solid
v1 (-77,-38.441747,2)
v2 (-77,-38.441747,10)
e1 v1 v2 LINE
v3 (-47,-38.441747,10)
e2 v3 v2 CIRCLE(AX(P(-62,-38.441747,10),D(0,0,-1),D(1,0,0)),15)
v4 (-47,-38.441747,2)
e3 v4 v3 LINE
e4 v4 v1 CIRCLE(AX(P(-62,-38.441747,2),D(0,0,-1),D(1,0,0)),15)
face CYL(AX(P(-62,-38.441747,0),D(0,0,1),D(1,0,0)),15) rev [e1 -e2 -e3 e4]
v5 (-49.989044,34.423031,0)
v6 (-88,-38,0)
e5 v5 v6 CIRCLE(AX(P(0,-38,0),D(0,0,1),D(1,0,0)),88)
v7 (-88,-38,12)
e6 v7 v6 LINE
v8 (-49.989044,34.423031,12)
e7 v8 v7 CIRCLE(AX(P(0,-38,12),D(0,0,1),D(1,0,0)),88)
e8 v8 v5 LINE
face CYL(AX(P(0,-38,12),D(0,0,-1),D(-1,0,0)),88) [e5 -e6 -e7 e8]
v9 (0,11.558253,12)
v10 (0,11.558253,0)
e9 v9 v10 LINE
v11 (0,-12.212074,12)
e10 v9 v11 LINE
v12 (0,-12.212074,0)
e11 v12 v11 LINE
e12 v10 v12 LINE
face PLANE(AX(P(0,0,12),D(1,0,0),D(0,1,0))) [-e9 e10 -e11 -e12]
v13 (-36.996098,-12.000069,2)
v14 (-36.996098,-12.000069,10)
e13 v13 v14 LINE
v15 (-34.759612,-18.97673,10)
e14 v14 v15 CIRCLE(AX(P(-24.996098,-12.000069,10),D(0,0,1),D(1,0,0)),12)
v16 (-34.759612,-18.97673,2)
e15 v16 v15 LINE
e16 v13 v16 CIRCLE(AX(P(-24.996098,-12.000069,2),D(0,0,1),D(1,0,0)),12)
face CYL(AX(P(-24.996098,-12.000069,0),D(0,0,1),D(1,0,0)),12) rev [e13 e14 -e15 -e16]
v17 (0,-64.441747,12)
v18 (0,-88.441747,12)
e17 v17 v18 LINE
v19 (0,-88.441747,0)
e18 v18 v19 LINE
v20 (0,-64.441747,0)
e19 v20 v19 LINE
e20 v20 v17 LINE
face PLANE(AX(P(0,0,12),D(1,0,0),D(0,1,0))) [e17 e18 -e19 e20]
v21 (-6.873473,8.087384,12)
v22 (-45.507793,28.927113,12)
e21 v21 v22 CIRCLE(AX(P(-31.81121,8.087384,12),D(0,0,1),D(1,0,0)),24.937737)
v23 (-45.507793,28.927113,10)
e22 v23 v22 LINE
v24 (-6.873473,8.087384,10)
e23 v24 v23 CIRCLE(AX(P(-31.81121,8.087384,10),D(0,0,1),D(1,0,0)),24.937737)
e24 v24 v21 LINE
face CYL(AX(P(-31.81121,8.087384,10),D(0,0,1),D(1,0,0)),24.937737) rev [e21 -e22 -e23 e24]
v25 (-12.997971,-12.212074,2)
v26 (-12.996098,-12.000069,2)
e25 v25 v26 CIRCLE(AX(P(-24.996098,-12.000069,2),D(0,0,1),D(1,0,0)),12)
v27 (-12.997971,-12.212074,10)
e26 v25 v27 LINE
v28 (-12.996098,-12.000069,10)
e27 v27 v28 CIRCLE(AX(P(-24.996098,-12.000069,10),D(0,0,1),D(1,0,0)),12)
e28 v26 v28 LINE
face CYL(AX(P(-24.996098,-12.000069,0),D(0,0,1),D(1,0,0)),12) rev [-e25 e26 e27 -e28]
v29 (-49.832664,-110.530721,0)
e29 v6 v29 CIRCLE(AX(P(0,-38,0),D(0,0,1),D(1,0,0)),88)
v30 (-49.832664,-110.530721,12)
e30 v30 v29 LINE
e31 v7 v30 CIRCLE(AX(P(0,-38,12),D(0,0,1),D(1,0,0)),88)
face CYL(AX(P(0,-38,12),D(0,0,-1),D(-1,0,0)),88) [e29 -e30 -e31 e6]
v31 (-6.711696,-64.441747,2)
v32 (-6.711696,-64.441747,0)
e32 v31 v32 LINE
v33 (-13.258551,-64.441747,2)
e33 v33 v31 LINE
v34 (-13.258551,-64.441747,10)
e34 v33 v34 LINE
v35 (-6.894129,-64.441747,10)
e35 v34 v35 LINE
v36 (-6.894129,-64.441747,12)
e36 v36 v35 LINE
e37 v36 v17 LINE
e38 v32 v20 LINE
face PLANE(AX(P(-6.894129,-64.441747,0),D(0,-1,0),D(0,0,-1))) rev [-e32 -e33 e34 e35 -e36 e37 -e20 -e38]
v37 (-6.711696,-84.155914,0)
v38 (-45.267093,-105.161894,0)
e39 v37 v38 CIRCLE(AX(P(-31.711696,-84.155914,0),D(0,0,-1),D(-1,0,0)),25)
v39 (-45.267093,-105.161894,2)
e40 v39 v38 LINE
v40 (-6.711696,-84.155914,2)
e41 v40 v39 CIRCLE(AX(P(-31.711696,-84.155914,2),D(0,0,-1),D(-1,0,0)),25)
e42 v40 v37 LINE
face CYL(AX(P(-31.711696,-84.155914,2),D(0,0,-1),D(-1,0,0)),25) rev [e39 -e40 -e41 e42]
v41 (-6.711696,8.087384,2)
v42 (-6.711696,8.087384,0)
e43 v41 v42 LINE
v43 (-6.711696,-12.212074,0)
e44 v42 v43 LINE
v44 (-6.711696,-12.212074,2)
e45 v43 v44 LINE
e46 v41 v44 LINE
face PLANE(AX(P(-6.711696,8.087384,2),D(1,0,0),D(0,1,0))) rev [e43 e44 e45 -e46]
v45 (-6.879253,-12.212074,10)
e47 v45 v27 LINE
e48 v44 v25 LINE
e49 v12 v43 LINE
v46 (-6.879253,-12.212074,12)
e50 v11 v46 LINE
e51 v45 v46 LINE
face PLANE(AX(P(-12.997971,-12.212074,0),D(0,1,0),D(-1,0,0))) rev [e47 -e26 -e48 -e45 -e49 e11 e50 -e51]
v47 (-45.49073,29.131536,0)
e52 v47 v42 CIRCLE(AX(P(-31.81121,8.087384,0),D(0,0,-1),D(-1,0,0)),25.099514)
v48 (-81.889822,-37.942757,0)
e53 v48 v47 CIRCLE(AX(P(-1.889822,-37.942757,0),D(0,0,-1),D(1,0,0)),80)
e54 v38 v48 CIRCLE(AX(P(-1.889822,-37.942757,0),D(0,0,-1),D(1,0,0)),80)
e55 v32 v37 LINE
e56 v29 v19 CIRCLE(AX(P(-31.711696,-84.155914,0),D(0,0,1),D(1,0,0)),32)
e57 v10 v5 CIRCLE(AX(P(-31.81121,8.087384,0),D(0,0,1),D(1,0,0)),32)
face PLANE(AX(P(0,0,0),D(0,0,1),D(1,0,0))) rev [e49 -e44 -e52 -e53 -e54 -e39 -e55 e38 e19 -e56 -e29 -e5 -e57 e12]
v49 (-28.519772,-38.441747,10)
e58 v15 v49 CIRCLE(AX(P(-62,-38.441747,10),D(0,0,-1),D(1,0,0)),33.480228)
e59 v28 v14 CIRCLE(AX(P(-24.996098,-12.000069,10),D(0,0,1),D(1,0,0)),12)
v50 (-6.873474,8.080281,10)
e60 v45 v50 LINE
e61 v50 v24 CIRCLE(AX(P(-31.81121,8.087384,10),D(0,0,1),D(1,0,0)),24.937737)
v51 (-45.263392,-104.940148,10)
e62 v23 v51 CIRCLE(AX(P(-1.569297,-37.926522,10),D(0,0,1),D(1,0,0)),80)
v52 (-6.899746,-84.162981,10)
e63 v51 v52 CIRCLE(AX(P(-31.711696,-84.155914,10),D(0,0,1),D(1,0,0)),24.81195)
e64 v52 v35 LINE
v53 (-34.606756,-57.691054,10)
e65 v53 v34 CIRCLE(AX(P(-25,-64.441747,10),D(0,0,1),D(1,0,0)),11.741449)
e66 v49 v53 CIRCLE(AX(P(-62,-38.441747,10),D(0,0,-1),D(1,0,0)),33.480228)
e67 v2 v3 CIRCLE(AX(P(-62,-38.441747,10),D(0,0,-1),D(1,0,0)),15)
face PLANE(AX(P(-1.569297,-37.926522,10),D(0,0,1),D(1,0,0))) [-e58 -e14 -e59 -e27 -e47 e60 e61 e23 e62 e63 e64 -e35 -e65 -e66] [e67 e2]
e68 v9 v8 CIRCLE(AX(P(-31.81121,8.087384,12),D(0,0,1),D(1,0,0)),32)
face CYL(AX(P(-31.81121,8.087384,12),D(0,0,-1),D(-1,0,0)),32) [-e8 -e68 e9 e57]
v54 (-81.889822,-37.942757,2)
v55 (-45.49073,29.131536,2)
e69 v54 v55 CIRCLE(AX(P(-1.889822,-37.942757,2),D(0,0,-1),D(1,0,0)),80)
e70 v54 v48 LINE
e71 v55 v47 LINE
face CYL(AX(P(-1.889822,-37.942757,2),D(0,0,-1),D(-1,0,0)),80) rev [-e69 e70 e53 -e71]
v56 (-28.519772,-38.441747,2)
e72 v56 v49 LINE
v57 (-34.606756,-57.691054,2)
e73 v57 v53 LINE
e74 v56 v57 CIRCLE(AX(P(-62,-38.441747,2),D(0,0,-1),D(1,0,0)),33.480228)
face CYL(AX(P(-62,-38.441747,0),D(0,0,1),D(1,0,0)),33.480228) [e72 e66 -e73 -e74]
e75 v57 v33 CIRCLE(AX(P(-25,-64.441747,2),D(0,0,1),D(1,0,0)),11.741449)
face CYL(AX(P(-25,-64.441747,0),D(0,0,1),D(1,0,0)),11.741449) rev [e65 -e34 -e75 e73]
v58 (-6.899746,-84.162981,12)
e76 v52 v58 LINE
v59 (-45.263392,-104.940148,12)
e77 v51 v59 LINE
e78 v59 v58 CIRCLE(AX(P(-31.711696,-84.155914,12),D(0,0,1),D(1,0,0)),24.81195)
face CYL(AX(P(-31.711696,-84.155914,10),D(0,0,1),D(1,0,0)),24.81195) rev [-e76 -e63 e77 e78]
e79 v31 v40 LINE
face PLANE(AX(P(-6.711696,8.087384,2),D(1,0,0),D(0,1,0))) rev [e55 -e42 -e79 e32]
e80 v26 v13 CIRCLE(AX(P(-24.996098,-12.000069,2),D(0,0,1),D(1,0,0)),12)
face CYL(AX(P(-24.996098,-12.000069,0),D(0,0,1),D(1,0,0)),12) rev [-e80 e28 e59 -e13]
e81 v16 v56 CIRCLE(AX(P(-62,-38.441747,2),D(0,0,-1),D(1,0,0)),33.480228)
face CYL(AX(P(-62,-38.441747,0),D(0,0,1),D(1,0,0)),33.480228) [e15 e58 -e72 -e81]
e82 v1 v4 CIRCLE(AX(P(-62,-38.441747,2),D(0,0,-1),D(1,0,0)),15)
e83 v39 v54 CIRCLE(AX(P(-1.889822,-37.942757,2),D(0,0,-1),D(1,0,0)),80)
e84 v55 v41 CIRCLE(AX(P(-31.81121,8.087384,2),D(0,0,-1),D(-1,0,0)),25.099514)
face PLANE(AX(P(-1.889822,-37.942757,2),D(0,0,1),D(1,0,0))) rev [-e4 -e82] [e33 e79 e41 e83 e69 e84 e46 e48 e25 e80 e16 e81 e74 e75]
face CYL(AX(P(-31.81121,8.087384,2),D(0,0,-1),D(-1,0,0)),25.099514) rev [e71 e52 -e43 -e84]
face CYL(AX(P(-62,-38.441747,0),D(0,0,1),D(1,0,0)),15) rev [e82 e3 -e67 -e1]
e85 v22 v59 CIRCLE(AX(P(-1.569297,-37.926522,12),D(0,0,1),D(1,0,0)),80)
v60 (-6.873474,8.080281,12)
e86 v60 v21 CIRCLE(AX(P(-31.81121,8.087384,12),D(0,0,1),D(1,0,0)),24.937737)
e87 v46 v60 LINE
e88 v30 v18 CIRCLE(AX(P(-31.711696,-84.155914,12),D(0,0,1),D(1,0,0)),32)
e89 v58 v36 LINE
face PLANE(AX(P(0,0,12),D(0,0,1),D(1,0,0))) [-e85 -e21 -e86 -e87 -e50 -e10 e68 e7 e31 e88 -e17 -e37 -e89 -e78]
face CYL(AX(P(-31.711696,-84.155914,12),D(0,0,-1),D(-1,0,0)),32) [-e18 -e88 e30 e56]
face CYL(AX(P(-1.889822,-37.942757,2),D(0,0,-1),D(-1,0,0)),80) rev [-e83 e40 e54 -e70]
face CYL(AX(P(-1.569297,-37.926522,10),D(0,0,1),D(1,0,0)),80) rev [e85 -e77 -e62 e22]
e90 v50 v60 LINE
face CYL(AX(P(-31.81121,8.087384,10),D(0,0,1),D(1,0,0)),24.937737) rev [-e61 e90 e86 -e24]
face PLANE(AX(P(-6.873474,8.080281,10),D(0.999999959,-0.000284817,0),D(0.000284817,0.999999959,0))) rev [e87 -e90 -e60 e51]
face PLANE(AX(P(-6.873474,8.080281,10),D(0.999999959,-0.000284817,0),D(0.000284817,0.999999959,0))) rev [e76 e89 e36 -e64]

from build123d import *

# Parameters (mm, degrees)
PLATE_BODY_12MM_DEPTH   = 12
THROUGH_HOLE_SKETCH_R   = 15
THROUGH_HOLE_DEPTH      = 12
FACE_POCKET_A_2MM_DEPTH = 2
FACE_POCKET_B_2MM_DEPTH = 2
SLOT_OPENING_CUT_DEPTH  = 10
RIM_NOTCH_A_SKETCH_W    = 6.711695518
RIM_NOTCH_A_SKETCH_H    = 52.229672595
RIM_NOTCH_A_DEPTH       = 10
RIM_NOTCH_B_SKETCH_W    = 2
RIM_NOTCH_B_SKETCH_H    = 52.229672595
RIM_NOTCH_B_DEPTH       = 10


with BuildPart() as part:
    # Plate Outline Sketch → Plate Body 12mm (new body)
    with BuildSketch(Plane.XY):
        with BuildLine():
            Line((0, -76), (0, 0))
            Line((0, 0), (0, 11.558252986))
            ThreePointArc((0, 11.558252986), (-10.446142685, 31.91035387), (-31.811209757, 40.087383673))
            ThreePointArc((-31.811209757, 40.087383673), (-41.331169578, 38.638494373), (-49.989043904, 34.423031486))
            ThreePointArc((-49.989043904, 34.423031486), (-87.99994879, -38.094936415), (-49.832664385, -110.530721493))
            ThreePointArc((-49.832664385, -110.530721493), (-41.198690561, -114.717276949), (-31.711695518, -116.155913677))
            ThreePointArc((-31.711695518, -116.155913677), (-10.653997006, -108.251003081), (0, -88.441747014))
            Line((0, -88.441747014), (0, -76))
        make_face()
    extrude(amount=PLATE_BODY_12MM_DEPTH)

    # Through Hole Sketch → Through Hole (cut)
    with BuildSketch(Plane.XY.offset(12)):
        with Locations((-62, -38.441747014)):
            Circle(THROUGH_HOLE_SKETCH_R)
    extrude(amount=-THROUGH_HOLE_DEPTH, mode=Mode.SUBTRACT)

    # Face Pocket A Sketch → Face Pocket A 2mm (cut)
    with BuildSketch(Plane.XY.offset(12)):
        with BuildLine():
            Line((-6.873473723, 8.080280991), (-6.899746136, -84.162980533))
            ThreePointArc((-6.899746136, -84.162980533), (-19.89556251, -105.973610229), (-45.263391889, -104.940148269))
            ThreePointArc((-45.263391889, -104.940148269), (-81.569163873, -38.072577616), (-45.50779291, 28.927113491))
            ThreePointArc((-45.50779291, 28.927113491), (-19.968976613, 30.033960698), (-6.873473723, 8.080280991))
        make_face()
    extrude(amount=-FACE_POCKET_A_2MM_DEPTH, mode=Mode.SUBTRACT)

    # Face Pocket B Sketch → Face Pocket B 2mm (cut)
    with BuildSketch(Plane(origin=(0, 0, 0), x_dir=(-1, 0, 0), z_dir=(0, 0, -1))):
        with BuildLine():
            Line((6.711695518, 8.087383673), (6.711695518, -84.155913677))
            ThreePointArc((6.711695518, -84.155913677), (19.751029382, -106.109101728), (45.267092765, -105.161893908))
            ThreePointArc((45.267092765, -105.161893908), (81.889710646, -38.07598005), (45.490730045, 29.131535823))
            ThreePointArc((45.490730045, 29.131535823), (19.839653868, 30.147924569), (6.711695518, 8.087383673))
        make_face()
    extrude(amount=-FACE_POCKET_B_2MM_DEPTH, mode=Mode.SUBTRACT)

    # Slot Opening Sketch → Slot Opening Cut (cut)
    with BuildSketch(Plane.XY.offset(10)):
        with BuildLine():
            Line((-12.997971015, -12.212074419), (-6.879253323, -12.212074419))
            Line((-6.879253323, -12.212074419), (0, -12.212074419))
            Line((0, -12.212074419), (0, -64.441747014))
            Line((0, -64.441747014), (-6.894129201, -64.441747014))
            Line((-6.894129201, -64.441747014), (-13.258551293, -64.441747014))
            ThreePointArc((-13.258551293, -64.441747014), (-28.540083812, -75.636809513), (-34.606755841, -57.691053721))
            ThreePointArc((-34.606755841, -57.691053721), (-28.520033449, -38.309557921), (-34.759611769, -18.976730106))
            ThreePointArc((-34.759611769, -18.976730106), (-28.558192424, -0.540946638), (-12.997971015, -12.212074419))
        make_face()
    extrude(amount=-SLOT_OPENING_CUT_DEPTH, mode=Mode.SUBTRACT)

    # Rim Notch A Sketch → Rim Notch A (cut)
    with BuildSketch(Plane(origin=(0, 0, 10), x_dir=(-1, 0, 0), z_dir=(0, 0, -1))):
        with Locations((3.355847759, -38.326910717)):
            Rectangle(RIM_NOTCH_A_SKETCH_W, RIM_NOTCH_A_SKETCH_H)
    extrude(amount=-RIM_NOTCH_A_DEPTH, mode=Mode.SUBTRACT)

    # Rim Notch B Sketch → Rim Notch B (cut)
    with BuildSketch(Plane(origin=(-6.711695518, 0, 0), x_dir=(0, 0, -1), z_dir=(1, 0, 0))):
        with Locations((-11, -38.326910717)):
            Rectangle(RIM_NOTCH_B_SKETCH_W, RIM_NOTCH_B_SKETCH_H)
    extrude(amount=-RIM_NOTCH_B_DEPTH, mode=Mode.SUBTRACT)


solid = part.part
